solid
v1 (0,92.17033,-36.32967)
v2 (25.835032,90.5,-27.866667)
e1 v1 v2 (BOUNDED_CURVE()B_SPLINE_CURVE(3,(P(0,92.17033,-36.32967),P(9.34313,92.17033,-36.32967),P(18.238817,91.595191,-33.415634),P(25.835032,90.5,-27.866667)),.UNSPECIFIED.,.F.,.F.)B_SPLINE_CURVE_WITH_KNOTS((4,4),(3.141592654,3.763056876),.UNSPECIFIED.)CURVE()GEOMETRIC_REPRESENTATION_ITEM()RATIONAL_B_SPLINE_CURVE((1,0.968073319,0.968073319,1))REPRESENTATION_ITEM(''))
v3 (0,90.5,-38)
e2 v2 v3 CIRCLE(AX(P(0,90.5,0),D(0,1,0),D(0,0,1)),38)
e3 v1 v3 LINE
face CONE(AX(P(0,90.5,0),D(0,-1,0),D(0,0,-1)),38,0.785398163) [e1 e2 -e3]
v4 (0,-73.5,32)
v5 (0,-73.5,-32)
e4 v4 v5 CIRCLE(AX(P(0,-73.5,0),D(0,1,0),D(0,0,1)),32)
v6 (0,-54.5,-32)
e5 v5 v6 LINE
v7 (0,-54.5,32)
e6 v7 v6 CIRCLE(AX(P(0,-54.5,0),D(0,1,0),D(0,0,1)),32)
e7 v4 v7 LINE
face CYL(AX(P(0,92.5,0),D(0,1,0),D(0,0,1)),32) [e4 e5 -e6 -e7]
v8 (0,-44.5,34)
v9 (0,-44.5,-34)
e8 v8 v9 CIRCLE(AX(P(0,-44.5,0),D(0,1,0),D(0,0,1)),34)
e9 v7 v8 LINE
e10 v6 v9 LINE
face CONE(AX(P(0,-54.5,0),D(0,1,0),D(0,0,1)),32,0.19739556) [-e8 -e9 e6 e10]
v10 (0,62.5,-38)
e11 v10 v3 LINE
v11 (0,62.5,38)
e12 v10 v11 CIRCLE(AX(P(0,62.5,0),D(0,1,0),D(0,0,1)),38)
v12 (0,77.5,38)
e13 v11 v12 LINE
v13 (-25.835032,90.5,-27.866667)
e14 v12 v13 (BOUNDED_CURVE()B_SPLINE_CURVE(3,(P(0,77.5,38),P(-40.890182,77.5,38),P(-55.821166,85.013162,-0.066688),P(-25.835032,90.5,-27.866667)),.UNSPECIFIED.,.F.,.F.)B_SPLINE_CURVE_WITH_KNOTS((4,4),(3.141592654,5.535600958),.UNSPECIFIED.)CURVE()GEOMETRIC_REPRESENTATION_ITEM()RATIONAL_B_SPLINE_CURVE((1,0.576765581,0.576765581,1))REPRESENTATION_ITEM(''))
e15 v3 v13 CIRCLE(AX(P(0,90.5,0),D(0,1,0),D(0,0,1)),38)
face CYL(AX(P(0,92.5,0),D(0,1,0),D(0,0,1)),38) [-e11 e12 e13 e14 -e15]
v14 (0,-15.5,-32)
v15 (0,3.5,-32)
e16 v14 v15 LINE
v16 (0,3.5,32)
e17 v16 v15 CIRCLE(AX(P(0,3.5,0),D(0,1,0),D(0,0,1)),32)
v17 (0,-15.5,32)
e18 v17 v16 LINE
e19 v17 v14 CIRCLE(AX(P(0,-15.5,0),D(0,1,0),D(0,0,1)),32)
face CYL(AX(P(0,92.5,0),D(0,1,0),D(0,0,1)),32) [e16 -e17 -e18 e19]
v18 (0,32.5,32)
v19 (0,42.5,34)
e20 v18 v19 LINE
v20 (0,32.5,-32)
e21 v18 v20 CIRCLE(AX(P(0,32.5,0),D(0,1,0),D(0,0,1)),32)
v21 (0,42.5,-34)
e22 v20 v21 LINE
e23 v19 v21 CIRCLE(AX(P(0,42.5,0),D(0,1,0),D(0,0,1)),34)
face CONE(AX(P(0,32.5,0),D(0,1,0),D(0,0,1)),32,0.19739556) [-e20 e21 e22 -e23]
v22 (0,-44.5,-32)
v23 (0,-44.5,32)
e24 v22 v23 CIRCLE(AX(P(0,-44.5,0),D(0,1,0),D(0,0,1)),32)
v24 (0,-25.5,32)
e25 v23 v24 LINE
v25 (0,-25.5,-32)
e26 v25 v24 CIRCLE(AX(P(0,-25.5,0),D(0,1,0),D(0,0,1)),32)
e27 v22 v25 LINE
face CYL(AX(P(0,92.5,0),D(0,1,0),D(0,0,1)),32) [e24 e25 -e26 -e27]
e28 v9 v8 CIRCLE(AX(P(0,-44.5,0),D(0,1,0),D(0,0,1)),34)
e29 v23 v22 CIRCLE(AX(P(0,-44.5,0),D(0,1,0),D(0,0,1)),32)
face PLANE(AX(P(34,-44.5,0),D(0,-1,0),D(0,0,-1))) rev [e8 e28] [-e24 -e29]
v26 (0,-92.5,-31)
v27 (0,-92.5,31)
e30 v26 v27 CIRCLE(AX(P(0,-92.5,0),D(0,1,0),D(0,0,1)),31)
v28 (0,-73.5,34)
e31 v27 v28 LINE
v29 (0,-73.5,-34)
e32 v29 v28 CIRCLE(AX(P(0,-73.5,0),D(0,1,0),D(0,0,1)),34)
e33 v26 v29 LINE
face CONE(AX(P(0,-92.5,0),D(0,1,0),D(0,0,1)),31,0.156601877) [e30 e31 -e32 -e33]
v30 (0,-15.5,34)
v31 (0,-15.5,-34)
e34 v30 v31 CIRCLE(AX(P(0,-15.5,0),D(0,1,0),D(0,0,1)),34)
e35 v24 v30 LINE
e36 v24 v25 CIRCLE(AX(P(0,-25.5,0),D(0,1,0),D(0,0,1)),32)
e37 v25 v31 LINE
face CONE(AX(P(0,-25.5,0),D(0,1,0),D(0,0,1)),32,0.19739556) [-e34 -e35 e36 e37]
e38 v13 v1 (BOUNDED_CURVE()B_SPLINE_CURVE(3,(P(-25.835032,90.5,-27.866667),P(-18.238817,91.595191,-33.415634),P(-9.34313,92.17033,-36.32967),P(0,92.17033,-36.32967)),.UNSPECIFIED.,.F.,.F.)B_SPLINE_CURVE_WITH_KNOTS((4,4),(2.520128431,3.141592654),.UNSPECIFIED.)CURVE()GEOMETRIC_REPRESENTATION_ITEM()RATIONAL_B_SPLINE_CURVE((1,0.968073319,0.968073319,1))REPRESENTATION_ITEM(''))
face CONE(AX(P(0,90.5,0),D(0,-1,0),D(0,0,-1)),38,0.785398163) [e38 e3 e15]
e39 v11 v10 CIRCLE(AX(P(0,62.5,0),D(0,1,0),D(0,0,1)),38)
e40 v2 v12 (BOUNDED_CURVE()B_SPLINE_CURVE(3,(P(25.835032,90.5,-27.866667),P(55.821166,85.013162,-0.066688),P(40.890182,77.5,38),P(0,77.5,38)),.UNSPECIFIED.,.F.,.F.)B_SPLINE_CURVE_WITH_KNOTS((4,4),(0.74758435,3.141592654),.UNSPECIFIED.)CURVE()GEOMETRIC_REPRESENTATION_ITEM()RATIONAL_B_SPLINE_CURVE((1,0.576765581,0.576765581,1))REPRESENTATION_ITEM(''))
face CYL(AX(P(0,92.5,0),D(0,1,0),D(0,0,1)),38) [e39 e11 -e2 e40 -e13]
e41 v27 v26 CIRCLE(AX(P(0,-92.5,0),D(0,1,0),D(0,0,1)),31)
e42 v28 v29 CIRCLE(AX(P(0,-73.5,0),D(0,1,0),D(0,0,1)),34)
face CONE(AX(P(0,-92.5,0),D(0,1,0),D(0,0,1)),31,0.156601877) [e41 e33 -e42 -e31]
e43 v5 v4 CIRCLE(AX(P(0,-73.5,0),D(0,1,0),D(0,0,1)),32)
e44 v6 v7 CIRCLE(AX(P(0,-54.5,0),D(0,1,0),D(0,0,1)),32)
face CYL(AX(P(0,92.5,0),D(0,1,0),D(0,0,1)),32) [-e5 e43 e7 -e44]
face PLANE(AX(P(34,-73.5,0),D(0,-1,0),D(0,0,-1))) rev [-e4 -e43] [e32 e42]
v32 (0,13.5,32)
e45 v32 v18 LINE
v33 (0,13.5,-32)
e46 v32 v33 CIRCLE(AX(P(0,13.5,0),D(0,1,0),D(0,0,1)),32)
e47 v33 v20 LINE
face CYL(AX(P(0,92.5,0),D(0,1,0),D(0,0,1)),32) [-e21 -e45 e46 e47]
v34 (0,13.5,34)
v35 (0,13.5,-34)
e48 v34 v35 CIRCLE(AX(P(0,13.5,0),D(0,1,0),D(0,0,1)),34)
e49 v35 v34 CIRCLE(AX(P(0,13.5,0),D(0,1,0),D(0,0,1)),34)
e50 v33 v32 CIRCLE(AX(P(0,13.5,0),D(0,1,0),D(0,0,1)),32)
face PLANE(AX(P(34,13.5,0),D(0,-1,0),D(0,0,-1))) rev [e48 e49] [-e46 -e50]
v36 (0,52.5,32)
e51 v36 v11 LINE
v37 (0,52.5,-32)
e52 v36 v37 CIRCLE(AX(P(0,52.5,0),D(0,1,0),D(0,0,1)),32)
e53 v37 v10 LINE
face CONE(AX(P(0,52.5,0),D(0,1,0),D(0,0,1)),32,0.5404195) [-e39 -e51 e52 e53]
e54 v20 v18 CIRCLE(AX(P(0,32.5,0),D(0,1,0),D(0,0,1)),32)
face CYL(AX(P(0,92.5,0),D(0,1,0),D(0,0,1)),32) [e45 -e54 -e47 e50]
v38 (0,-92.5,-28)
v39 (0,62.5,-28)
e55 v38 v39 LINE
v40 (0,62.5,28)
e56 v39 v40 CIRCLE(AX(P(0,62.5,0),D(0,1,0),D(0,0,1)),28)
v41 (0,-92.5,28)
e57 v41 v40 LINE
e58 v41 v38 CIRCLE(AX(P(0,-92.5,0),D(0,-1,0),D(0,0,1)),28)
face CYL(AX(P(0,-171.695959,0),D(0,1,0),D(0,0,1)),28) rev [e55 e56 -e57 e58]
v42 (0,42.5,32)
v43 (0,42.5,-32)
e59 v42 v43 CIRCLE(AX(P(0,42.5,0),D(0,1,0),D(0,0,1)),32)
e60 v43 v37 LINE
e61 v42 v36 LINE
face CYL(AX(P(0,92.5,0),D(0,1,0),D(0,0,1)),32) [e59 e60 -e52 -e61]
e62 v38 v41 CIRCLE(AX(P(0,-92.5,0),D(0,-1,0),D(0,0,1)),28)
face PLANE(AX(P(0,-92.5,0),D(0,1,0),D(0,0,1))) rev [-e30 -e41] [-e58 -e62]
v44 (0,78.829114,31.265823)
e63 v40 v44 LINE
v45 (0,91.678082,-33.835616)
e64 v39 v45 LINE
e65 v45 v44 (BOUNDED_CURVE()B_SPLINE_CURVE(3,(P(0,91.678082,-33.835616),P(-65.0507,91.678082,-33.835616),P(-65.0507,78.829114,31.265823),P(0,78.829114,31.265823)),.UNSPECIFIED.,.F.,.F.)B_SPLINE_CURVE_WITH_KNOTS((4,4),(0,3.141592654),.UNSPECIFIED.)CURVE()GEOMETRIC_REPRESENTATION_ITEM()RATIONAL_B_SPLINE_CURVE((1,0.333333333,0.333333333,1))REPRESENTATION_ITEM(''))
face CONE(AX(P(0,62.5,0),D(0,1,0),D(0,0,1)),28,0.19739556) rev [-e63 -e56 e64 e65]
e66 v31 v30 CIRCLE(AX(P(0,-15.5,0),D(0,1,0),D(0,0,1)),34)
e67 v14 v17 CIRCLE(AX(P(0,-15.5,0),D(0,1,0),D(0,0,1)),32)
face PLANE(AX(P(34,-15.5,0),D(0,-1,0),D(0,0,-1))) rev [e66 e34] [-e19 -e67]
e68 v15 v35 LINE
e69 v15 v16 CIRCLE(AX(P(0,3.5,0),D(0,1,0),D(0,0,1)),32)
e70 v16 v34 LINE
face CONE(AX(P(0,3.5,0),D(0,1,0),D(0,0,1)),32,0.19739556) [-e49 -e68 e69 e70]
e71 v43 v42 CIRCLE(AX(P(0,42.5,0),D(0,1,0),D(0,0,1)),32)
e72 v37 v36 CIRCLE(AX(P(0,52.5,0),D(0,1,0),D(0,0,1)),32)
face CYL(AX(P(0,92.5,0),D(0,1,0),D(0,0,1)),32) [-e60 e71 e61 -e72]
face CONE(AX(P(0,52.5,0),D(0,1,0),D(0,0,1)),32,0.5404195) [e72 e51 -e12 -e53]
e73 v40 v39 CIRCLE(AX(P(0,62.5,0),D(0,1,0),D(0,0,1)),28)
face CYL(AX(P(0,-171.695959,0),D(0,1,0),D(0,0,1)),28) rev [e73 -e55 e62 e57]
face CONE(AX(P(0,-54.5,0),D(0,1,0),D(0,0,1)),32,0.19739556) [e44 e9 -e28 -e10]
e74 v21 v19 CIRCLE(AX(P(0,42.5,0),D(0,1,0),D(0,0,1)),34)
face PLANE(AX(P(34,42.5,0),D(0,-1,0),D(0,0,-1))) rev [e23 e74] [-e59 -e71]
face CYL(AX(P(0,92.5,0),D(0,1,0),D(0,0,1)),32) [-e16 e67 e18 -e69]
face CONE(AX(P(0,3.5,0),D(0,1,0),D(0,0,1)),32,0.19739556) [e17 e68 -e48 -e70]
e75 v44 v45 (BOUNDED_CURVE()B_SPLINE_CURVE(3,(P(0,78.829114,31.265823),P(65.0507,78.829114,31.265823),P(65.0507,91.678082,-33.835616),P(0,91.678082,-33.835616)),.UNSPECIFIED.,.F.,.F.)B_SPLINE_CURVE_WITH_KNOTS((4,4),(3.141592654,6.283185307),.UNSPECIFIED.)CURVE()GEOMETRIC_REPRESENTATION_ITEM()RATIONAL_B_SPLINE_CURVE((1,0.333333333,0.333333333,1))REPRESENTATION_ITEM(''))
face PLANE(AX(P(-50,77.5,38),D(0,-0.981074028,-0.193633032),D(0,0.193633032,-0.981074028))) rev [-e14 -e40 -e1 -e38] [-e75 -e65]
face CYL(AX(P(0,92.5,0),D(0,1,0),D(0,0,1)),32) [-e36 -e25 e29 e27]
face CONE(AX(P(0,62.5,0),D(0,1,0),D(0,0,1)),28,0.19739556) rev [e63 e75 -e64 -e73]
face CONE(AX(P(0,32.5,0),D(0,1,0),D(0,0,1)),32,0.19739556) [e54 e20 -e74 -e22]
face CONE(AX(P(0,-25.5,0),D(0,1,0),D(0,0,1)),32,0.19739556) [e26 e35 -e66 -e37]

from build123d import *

# Parameters (mm, degrees)
SKETCH_2_R          = 28
CUT_EXTRUDE_1_DEPTH = 185
SKETCH_4_R          = 34
SKETCH_3_R          = 28
CUT_EXTRUDE_2_DEPTH = 50


with BuildPart() as part:
    # 草图1 → 旋转1 (revolve)
    with BuildSketch(Plane.XY, mode=Mode.PRIVATE) as revolve_1_sk:
        Polygon((0, 92.5), (0, -92.5), (31, -92.5), (34, -73.5), (32, -73.5), (32, -54.5), (34, -44.5), (32, -44.5), (32, -25.5), (34, -15.5), (32, -15.5), (32, 3.5), (34, 13.5), (32, 13.5), (32, 32.5), (34, 42.5), (32, 42.5), (32, 52.5), (38, 62.5), (38, 90.5), (36, 92.5), align=None)
    revolve(revolve_1_sk.sketch.rotate(Axis((0, 92.5, 0), (0, -1, 0)), 90), axis=Axis((0, 92.5, 0), (0, -1, 0)))

    # 草图2 → 切除-拉伸1 (cut)
    with BuildSketch(Plane(origin=(0, 92.5, 0), x_dir=(1, 0, 0), z_dir=(0, 1, 0))):
        with Locations(Location((0, 0, 0), (0, 0, 270))):
            Circle(SKETCH_2_R)
    extrude(amount=-CUT_EXTRUDE_1_DEPTH, mode=Mode.SUBTRACT)

    # 草图4 → 切除-放样1 section 0
    with BuildSketch(Plane(origin=(0, 92.5, 0), x_dir=(1, 0, 0), z_dir=(0, 1, 0))):
        Circle(SKETCH_4_R)
    # 草图3 → 切除-放样1 section 1
    with BuildSketch(Plane(origin=(0, 62.5, 0), x_dir=(-1, 0, 0), z_dir=(0, 1, 0))):
        Circle(SKETCH_3_R)
    loft(mode=Mode.SUBTRACT)

    # 草图5 → 切除-拉伸2 (cut, symmetric)
    with BuildSketch(Plane(origin=(0, 0, 0), x_dir=(0, 0, -1), z_dir=(1, 0, 0))):
        Polygon((-38, 77.5), (38, 92.5), (-38, 92.5), align=None)
    extrude(amount=CUT_EXTRUDE_2_DEPTH, both=True, mode=Mode.SUBTRACT)


solid = part.part
